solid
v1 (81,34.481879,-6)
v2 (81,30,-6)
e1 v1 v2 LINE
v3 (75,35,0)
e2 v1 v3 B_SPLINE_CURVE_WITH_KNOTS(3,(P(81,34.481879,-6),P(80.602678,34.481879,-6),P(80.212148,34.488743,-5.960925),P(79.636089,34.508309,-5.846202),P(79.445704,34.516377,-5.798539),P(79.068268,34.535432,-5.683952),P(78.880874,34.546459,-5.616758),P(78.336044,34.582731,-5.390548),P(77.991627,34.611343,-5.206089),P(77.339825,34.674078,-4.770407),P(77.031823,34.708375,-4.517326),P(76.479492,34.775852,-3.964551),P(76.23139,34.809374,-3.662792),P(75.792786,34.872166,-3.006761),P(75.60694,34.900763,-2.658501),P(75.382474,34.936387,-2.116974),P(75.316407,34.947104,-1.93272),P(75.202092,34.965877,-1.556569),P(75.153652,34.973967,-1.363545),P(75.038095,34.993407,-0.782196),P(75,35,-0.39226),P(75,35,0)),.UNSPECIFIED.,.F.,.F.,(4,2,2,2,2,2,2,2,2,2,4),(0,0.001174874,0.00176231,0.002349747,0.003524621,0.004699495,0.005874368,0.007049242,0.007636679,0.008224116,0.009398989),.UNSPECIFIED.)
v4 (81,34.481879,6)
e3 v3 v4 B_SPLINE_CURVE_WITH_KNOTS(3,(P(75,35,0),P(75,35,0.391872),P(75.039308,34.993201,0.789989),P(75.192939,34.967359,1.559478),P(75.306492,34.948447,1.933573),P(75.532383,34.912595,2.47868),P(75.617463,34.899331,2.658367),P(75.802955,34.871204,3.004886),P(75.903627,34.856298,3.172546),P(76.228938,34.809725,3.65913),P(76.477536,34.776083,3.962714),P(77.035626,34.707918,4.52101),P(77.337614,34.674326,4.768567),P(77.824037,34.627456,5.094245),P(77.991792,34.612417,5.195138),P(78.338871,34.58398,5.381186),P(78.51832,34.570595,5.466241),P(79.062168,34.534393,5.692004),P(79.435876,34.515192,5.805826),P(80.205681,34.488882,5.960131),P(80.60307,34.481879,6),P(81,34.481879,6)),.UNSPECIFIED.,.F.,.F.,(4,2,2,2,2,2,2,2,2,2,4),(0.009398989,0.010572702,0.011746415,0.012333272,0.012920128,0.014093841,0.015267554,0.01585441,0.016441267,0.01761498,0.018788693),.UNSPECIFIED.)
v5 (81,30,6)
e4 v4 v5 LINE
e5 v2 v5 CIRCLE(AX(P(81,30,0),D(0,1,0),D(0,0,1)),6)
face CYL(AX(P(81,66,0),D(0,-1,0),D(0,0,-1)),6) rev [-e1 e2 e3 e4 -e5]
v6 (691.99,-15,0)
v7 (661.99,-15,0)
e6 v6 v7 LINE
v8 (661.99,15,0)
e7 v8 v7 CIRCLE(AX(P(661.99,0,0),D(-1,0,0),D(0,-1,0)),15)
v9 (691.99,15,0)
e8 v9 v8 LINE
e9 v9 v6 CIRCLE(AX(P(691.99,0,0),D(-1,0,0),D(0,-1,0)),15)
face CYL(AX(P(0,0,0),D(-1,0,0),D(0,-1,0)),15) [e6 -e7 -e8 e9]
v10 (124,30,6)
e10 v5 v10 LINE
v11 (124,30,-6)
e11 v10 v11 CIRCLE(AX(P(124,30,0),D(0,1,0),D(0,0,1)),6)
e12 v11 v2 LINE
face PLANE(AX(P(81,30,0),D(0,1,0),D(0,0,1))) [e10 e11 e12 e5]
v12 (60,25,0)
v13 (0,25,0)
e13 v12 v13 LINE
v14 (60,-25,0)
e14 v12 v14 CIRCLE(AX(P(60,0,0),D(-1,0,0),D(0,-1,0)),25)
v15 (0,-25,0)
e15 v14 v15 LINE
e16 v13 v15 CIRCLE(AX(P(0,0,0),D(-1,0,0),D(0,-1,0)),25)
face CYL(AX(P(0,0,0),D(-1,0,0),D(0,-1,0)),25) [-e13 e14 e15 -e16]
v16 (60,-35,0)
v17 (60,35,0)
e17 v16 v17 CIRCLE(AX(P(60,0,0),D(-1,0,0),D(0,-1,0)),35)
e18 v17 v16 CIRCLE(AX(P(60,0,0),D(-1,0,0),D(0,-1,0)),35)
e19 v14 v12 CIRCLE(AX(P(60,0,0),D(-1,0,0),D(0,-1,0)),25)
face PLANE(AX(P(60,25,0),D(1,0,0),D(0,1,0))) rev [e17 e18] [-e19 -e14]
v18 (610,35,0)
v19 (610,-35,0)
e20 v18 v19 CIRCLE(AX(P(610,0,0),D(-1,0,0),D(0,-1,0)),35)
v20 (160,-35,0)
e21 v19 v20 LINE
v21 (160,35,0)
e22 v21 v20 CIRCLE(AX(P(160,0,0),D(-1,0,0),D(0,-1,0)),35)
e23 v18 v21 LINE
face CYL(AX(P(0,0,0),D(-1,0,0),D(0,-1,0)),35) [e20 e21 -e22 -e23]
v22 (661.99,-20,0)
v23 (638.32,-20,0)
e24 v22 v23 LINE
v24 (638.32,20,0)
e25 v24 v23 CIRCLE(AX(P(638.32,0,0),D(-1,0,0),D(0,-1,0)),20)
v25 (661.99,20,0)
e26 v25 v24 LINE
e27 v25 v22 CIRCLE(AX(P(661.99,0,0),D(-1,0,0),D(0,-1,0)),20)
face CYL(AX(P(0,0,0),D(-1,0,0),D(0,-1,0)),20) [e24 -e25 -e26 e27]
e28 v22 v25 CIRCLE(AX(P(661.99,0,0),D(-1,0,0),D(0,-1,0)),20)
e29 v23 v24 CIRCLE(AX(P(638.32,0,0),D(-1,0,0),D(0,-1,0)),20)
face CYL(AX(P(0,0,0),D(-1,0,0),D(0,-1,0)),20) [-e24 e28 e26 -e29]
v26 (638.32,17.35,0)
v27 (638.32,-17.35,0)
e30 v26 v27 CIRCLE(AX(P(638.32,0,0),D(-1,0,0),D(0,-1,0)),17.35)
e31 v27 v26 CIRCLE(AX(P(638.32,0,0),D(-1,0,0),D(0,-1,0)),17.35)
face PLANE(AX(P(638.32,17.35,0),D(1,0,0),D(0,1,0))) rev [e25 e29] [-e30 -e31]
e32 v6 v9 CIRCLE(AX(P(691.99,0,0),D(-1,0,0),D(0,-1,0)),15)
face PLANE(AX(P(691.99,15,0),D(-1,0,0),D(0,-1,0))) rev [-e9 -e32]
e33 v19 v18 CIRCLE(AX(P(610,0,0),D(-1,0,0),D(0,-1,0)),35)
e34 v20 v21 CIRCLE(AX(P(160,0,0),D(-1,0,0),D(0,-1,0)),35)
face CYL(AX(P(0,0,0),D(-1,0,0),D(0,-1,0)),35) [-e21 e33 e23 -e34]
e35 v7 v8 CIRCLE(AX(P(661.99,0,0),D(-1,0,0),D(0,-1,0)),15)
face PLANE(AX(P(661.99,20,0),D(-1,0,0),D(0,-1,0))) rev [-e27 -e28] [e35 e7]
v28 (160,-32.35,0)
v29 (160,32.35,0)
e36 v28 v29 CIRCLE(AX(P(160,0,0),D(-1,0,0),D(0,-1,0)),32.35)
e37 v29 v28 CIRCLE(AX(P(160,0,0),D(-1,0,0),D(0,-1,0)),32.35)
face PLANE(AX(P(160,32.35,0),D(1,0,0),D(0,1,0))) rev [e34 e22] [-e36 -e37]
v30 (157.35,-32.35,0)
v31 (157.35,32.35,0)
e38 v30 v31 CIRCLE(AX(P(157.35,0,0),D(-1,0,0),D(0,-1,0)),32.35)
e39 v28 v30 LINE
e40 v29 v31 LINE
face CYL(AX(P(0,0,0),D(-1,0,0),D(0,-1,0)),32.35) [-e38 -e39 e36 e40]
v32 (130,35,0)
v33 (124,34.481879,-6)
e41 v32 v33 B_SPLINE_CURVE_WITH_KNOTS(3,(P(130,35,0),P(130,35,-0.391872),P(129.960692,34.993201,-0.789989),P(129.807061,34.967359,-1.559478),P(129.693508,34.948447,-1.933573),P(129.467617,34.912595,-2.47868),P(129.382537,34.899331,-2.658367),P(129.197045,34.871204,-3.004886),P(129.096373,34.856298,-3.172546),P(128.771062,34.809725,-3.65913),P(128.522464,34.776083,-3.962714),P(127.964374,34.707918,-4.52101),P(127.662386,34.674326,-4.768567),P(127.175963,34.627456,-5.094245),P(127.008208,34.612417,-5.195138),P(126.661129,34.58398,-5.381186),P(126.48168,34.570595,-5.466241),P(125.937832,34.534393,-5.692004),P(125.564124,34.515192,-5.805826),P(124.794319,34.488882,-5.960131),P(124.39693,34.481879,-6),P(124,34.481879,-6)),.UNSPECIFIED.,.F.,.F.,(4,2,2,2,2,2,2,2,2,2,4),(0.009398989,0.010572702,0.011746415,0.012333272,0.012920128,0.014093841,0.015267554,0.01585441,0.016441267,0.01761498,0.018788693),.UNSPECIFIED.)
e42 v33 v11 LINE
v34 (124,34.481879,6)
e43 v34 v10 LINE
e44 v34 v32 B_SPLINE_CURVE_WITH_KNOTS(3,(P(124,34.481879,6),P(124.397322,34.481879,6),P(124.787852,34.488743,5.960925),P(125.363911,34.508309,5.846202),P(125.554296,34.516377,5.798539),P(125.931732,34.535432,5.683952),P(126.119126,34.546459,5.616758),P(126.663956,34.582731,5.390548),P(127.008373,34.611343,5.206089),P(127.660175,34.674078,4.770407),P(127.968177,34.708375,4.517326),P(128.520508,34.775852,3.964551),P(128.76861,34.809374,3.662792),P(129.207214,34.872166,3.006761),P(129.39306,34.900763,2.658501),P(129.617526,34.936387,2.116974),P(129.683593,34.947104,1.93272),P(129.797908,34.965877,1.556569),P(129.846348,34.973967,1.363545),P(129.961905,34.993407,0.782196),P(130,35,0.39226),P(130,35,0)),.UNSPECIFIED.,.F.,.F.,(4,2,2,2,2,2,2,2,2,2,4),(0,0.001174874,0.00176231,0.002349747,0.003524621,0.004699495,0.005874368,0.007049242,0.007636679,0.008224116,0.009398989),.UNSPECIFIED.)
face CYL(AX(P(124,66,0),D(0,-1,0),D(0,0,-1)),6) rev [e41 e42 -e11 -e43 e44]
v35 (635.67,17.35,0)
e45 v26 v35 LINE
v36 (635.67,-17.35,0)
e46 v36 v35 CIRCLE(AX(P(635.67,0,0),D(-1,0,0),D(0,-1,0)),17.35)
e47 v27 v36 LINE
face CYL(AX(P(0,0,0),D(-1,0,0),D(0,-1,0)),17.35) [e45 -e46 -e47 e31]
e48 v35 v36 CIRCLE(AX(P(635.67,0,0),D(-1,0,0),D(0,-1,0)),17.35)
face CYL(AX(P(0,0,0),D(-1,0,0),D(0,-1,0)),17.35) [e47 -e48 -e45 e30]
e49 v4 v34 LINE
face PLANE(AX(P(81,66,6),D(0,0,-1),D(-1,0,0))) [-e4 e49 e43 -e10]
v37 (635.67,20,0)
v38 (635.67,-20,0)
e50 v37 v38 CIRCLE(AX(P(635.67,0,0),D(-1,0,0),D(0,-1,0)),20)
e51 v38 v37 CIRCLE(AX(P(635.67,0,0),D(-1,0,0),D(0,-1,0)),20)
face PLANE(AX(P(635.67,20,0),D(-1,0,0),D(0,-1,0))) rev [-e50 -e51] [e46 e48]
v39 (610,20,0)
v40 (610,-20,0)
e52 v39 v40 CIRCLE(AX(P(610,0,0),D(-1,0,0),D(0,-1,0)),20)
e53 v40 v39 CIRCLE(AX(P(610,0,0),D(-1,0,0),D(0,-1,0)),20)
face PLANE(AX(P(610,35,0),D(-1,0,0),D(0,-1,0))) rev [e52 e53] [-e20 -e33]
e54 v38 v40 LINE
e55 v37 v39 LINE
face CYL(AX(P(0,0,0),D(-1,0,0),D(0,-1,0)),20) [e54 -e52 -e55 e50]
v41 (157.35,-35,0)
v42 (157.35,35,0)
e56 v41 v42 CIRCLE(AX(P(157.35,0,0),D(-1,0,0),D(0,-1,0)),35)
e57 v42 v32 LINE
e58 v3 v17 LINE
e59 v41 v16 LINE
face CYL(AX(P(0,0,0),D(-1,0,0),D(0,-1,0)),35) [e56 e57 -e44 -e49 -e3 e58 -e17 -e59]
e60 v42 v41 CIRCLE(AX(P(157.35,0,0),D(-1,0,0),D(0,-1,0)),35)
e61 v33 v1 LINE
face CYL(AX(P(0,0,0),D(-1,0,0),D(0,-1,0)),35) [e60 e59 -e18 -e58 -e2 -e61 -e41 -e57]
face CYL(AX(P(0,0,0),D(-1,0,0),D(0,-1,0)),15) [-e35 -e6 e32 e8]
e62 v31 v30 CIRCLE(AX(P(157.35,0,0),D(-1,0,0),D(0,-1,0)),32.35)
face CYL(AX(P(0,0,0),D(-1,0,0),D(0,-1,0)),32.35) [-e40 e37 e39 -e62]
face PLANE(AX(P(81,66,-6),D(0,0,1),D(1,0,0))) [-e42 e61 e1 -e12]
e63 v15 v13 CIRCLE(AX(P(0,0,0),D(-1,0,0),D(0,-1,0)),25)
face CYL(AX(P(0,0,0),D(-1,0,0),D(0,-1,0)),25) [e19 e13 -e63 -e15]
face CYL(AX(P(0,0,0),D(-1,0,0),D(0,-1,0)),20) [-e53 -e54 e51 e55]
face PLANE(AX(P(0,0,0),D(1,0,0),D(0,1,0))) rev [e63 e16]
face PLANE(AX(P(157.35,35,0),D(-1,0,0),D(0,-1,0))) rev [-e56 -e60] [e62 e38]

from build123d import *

# Parameters (mm, degrees)
CUT_EXTRUDE1_DEPTH      = 1
CUT_EXTRUDE1_DEPTH_BACK = 35
CUT_EXTRUDE1_START      = 65


with BuildPart() as part:
    # Sketch1 → Revolve1 (revolve)
    with BuildSketch(Plane.XY, mode=Mode.PRIVATE) as revolve1_sk:
        Polygon((0, 0), (0, 25), (60, 25), (60, 35), (157.35, 35), (157.35, 32.35), (160, 32.35), (160, 35), (610, 35), (610, 20), (635.67, 20), (635.67, 17.35), (638.32, 17.35), (638.32, 20), (661.99, 20), (661.99, 15), (691.99, 15), (691.99, 0), align=None)
    revolve(revolve1_sk.sketch.rotate(Axis((0, 0, 0), (1, 0, 0)), 180), axis=Axis((0, 0, 0), (1, 0, 0)))

    # Sketch2 → Cut-Extrude1 (cut, two sides: drawn at the far end of the back side and taken through both)
    with BuildSketch(Plane(origin=(0, 0, 0), x_dir=(1, 0, 0), z_dir=(0, 1, 0)).offset(CUT_EXTRUDE1_START - CUT_EXTRUDE1_DEPTH_BACK)):
        with BuildLine():
            Line((81, 6), (124, 6))
            ThreePointArc((124, 6), (130, 0), (124, -6))
            Line((124, -6), (81, -6))
            ThreePointArc((81, -6), (75, 0), (81, 6))
        make_face()
    extrude(amount=CUT_EXTRUDE1_DEPTH + CUT_EXTRUDE1_DEPTH_BACK, mode=Mode.SUBTRACT)


solid = part.part
